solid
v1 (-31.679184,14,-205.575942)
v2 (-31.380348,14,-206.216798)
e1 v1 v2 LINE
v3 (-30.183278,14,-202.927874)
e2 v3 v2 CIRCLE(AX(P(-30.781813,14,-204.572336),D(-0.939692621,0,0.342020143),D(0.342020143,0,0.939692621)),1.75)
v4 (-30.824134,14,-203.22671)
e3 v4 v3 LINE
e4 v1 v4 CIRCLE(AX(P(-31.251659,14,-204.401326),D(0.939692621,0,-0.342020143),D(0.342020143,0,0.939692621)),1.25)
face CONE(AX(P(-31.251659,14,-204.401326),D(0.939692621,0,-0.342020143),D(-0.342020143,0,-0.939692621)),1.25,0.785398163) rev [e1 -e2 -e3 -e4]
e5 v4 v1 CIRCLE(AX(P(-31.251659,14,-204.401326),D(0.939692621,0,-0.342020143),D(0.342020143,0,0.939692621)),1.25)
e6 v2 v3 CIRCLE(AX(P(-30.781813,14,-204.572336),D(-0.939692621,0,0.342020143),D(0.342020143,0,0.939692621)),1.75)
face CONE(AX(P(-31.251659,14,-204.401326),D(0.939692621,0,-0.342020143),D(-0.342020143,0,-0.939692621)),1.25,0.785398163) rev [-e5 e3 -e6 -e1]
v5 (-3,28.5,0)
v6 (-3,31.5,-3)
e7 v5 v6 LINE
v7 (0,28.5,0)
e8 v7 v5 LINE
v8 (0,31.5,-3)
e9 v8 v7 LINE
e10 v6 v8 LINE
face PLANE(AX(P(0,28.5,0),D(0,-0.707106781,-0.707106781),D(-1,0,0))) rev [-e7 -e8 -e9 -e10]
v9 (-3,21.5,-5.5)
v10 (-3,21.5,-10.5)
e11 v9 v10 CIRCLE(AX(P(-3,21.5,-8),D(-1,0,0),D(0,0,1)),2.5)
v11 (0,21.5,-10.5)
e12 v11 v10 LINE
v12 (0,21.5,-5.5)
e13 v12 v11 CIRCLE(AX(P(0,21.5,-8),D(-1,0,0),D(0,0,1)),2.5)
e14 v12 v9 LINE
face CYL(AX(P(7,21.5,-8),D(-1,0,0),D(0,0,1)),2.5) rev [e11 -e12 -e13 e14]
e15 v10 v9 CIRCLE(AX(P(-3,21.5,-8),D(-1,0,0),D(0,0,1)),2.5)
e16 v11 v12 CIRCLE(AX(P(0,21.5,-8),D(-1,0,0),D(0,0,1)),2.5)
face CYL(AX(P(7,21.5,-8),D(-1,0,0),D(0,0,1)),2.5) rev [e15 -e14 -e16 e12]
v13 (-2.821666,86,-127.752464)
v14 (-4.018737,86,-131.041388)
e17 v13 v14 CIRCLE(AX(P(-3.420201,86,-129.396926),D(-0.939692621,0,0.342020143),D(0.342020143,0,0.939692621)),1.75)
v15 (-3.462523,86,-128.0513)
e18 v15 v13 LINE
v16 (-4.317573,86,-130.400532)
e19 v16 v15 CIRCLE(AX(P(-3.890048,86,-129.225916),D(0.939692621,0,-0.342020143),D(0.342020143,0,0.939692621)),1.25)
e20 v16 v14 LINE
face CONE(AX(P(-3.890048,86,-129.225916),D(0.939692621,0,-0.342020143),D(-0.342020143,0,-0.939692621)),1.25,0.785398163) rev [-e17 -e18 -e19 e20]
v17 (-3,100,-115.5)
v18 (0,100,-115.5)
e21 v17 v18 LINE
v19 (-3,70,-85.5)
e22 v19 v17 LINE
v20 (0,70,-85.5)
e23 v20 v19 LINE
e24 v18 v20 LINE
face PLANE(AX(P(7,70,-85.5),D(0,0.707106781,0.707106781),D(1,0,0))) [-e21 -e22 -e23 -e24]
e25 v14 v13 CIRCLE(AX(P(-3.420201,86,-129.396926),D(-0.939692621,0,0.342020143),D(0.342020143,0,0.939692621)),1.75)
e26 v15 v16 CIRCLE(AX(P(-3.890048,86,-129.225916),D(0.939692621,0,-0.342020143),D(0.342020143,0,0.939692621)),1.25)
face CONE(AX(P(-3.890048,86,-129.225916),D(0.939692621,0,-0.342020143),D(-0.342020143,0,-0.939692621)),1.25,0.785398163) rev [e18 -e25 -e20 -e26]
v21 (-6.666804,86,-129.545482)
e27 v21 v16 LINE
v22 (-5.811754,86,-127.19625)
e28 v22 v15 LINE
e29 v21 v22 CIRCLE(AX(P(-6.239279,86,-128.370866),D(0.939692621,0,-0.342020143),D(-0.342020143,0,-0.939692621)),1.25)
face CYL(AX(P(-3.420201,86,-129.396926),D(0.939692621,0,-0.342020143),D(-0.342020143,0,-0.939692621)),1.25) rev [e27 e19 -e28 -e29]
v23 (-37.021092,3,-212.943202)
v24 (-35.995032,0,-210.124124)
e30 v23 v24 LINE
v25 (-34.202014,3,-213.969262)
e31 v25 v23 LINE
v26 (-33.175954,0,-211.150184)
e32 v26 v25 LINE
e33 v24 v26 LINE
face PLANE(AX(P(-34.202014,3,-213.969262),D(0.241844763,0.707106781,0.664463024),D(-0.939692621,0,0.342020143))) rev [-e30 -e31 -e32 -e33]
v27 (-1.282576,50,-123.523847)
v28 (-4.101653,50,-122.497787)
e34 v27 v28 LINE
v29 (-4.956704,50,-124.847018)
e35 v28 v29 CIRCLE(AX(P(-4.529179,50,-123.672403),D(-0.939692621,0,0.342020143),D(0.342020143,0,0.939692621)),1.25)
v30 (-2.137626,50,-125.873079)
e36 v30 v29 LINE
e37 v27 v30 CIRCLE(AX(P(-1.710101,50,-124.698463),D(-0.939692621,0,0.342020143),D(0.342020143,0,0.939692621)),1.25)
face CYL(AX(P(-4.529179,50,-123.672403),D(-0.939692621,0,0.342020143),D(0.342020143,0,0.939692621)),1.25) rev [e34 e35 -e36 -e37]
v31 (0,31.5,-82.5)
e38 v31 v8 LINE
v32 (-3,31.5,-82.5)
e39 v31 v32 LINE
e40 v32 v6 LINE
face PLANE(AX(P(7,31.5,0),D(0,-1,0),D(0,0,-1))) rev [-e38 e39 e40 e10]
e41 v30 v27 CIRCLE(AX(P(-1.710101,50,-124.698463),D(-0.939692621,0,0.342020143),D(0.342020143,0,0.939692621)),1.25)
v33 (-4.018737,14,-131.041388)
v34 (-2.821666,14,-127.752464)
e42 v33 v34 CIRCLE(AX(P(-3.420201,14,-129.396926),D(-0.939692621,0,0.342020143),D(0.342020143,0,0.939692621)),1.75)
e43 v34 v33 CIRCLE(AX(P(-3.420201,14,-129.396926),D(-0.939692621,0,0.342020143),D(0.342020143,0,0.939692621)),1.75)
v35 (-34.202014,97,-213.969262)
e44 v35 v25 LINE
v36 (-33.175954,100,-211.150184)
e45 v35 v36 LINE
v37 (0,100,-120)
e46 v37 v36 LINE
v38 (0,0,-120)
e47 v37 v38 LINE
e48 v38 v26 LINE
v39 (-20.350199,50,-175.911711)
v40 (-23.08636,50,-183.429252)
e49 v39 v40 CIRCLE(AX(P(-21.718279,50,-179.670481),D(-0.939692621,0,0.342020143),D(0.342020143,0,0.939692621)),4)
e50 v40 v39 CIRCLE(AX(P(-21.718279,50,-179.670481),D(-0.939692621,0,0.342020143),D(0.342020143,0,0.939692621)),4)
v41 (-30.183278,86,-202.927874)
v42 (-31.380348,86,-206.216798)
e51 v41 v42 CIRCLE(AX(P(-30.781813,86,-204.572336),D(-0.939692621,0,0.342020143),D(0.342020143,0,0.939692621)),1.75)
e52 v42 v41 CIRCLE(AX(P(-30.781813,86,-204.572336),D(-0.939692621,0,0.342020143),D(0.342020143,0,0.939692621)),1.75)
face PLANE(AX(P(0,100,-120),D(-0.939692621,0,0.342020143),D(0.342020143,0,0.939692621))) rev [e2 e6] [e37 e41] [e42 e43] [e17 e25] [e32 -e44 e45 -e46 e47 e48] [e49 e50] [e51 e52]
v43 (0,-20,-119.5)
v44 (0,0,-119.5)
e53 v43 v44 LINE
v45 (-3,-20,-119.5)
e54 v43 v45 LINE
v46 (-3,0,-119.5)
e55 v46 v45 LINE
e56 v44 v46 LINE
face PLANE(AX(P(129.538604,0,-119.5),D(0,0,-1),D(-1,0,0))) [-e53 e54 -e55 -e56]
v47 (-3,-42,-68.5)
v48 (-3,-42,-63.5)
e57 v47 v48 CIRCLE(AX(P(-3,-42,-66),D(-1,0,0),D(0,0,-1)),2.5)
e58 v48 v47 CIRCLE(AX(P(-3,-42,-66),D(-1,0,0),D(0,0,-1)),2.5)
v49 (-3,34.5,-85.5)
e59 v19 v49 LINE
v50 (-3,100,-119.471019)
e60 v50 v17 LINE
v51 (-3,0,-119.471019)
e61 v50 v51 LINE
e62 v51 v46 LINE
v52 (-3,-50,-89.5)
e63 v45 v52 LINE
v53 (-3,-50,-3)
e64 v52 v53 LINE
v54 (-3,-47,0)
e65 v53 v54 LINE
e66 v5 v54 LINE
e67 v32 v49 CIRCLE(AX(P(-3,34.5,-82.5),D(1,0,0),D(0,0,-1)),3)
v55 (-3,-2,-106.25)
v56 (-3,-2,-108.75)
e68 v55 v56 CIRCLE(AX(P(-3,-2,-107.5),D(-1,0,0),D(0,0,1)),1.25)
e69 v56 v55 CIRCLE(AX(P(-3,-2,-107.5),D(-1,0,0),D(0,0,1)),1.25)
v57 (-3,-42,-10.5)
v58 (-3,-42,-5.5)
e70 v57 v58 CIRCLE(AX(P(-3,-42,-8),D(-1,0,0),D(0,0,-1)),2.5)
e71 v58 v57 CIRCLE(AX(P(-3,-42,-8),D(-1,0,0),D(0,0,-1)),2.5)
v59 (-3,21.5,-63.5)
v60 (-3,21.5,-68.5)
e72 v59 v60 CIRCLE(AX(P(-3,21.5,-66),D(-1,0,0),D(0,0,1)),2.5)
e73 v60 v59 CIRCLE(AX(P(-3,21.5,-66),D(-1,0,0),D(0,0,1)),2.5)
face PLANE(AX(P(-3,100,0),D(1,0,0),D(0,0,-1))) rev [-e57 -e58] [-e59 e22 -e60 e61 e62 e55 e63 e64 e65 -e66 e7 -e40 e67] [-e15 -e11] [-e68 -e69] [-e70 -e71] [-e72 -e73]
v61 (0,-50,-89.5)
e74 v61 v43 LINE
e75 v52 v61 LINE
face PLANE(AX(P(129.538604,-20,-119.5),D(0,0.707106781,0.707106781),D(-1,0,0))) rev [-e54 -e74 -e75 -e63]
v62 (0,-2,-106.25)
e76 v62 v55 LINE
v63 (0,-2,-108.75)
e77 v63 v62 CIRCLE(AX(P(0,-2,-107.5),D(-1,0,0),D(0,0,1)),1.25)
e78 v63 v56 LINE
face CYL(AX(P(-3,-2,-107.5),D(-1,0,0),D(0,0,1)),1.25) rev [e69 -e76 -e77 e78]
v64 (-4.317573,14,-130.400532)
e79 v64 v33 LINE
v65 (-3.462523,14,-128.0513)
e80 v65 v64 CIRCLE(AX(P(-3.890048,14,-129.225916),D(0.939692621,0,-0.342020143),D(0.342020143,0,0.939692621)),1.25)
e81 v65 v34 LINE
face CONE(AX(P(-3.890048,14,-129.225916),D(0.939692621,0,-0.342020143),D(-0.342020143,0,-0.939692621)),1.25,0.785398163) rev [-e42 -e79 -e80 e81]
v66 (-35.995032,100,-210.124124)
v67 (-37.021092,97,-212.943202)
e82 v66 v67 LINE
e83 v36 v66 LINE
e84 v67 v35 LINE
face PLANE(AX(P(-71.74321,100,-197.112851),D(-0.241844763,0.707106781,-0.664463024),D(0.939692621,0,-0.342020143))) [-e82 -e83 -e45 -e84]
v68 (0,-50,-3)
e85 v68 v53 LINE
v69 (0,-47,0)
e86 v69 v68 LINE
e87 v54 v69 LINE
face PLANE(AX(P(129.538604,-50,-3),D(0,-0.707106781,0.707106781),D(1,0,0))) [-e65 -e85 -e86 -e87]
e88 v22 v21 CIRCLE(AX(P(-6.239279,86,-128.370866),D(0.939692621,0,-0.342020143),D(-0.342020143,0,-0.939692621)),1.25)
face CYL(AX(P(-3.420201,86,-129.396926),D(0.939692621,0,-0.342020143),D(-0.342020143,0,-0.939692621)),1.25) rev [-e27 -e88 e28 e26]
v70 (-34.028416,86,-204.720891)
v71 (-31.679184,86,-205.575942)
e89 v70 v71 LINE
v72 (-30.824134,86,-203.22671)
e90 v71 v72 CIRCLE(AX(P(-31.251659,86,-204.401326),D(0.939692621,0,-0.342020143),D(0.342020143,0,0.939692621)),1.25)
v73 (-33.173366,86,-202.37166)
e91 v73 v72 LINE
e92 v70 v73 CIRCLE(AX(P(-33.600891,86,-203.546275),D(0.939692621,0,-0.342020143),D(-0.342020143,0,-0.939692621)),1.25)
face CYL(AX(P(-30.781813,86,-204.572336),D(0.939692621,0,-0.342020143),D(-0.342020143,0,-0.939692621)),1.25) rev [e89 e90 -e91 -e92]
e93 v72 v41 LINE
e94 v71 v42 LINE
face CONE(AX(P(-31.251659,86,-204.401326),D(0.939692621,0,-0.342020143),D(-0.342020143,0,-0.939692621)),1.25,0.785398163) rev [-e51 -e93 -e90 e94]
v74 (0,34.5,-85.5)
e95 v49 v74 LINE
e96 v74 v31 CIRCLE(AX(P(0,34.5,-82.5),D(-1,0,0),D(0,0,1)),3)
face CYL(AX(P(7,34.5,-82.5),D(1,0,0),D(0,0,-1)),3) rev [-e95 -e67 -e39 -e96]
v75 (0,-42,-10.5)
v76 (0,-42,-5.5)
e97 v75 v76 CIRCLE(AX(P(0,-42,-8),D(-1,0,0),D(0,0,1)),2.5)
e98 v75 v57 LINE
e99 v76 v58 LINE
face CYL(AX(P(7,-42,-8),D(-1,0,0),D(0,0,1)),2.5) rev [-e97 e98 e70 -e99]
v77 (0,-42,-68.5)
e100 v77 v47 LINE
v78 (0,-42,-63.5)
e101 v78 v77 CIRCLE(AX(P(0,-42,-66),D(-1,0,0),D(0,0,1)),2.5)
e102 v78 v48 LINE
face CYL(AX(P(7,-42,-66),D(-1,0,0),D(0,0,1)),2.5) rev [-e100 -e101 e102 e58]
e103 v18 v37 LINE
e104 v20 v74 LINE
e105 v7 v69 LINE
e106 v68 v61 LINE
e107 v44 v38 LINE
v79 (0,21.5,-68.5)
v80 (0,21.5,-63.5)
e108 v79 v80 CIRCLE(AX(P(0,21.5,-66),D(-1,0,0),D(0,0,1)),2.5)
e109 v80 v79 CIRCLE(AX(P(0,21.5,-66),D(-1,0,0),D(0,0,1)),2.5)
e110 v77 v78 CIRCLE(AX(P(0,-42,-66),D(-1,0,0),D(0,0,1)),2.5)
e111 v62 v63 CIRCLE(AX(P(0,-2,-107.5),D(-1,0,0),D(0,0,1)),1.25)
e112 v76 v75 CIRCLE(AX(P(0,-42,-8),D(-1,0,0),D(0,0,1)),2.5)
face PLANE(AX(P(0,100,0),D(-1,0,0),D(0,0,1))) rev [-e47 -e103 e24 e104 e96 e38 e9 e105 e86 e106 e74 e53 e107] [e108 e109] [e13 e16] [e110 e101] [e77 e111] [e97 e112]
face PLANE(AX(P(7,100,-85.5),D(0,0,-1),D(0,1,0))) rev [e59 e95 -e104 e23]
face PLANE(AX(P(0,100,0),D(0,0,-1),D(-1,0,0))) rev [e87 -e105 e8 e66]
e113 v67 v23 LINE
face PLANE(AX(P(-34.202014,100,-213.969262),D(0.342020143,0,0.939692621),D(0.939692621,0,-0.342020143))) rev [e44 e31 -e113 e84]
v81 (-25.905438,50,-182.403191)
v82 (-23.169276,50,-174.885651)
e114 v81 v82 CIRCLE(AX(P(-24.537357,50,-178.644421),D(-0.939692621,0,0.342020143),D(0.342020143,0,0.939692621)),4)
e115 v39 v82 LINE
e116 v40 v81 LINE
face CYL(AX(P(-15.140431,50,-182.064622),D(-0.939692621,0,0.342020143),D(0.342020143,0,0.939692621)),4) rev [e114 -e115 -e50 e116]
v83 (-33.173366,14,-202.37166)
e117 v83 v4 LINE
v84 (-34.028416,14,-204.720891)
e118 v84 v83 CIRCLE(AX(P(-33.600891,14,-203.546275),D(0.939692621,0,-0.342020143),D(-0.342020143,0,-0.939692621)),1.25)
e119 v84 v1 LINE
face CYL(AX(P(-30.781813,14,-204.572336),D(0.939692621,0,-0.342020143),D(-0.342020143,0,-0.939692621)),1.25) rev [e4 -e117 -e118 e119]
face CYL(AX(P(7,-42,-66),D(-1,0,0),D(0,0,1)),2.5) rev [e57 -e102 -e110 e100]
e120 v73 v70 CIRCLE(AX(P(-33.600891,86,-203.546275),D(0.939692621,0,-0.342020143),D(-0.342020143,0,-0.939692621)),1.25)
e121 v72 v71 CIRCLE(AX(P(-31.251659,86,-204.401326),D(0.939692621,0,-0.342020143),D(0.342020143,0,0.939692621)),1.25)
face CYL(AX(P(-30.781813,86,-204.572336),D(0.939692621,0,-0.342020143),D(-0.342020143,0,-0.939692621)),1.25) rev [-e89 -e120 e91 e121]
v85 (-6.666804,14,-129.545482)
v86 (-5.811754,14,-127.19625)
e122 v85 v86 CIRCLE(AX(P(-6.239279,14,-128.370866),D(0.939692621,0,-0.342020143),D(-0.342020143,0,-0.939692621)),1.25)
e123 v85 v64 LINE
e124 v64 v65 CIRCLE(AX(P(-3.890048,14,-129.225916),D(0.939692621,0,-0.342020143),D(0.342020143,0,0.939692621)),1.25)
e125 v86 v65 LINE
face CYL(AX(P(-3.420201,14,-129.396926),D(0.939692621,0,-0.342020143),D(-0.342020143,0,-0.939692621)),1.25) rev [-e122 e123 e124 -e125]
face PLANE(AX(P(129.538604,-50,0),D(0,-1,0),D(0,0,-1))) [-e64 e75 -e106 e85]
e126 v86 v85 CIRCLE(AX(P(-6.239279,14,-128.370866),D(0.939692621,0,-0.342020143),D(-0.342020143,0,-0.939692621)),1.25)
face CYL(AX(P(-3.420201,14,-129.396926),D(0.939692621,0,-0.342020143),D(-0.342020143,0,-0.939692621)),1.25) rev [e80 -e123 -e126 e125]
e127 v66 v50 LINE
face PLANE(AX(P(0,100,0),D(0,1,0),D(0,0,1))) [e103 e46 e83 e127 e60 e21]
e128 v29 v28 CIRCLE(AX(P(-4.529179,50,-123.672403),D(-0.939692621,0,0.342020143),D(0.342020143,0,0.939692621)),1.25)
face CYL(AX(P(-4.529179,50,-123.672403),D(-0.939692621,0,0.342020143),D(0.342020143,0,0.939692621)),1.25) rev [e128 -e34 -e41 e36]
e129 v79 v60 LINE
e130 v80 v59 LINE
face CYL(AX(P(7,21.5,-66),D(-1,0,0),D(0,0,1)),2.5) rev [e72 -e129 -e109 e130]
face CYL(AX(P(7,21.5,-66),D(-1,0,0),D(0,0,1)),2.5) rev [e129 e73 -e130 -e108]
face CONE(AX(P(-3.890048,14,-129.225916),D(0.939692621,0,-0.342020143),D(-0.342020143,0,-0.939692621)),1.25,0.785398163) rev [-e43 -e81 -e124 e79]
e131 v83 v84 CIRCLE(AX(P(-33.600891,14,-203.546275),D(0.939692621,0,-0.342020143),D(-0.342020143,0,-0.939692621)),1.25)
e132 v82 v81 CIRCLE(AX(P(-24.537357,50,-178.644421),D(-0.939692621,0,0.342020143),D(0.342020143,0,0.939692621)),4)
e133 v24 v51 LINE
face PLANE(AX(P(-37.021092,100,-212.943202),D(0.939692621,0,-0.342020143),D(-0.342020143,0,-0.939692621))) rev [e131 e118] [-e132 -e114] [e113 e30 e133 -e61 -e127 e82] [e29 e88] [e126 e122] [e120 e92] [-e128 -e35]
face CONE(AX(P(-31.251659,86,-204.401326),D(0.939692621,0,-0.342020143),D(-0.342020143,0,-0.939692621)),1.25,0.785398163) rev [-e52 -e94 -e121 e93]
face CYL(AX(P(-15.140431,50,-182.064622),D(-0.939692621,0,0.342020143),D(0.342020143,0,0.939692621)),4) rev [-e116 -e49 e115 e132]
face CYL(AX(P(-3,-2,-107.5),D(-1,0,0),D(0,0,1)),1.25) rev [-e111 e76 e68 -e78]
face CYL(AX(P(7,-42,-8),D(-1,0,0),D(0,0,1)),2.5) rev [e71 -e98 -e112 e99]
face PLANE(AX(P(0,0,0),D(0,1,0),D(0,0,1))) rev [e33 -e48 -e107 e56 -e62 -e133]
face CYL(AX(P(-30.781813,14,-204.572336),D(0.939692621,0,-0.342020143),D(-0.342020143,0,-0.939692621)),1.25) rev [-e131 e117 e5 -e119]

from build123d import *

# Parameters (mm, degrees)
BOSS_EXTRUDE1_DEPTH   = 100
SKETCH3_R             = 1
CUT_EXTRUDE2_DEPTH    = 10
LPATTERN1_COUNT       = 2
LPATTERN1_PITCH       = 80
M3_TAPPED_HOLE1_D     = 2.5
M3_TAPPED_HOLE1_DEPTH = 7.5
M3_TAPPED_HOLE1_TIP   = 0.751075774
CHAMFER2_SIZE         = 0.5
SKETCH6_W             = 85.5
SKETCH6_H             = 68.5
CUT_EXTRUDE4_DEPTH    = 10
CHAMFER3_SIZE         = 30
FILLET1_R             = 3
SKETCH7_R             = 4
CUT_EXTRUDE5_DEPTH    = 10
SKETCH9_W             = 119.5
SKETCH9_H             = 50
BOSS_EXTRUDE2_DEPTH   = 3
SKETCH5_R             = 2.5
CUT_EXTRUDE3_DEPTH    = 10
CHAMFER4_SIZE         = 3
CHAMFER5_SIZE         = 30
M3_TAPPED_HOLE2_D     = 2.5
M3_TAPPED_HOLE2_DEPTH = 7.5
M3_TAPPED_HOLE2_TIP   = 0.751075774
M3_TAPPED_HOLE3_D     = 2.5
M3_TAPPED_HOLE3_DEPTH = 7.5
M3_TAPPED_HOLE3_TIP   = 0.751075774


with BuildPart() as part:
    # Sketch1 → Boss-Extrude1 (new body)
    with BuildSketch(Plane(origin=(0, 0, 0), x_dir=(1, 0, 0), z_dir=(0, 1, 0))):
        Polygon((0, 120), (-34.202014333, 213.969262079), (-37.021092195, 212.943201649), (-3, 119.471019058), (-3, 0), (0, 0), align=None)
    extrude(amount=BOSS_EXTRUDE1_DEPTH)

    # Sketch3 → Cut-Extrude2 (cut)
    with BuildSketch(Plane(origin=(35.748178719, 0, -13.011272983), x_dir=(0.3420201433256699, 0, 0.939692620785908), z_dir=(-0.9396926207859081, 0, 0.3420201433256699))):
        with Locations((-202.763114494, 86)):
            Circle(SKETCH3_R)
        with Locations((-202.763114494, 14)):
            Circle(SKETCH3_R)
    cut_extrude2 = extrude(amount=-CUT_EXTRUDE2_DEPTH, mode=Mode.SUBTRACT)

    # LPattern1: Cut-Extrude2 ×2
    with Locations(*[Vector(0.3420201433256699, 0, 0.939692620785908) * (i * LPATTERN1_PITCH) for i in range(1, LPATTERN1_COUNT)]):
        add(cut_extrude2, mode=Mode.SUBTRACT)

    # M3 Tapped Hole1
    with Locations(Plane(origin=(-30.781812899, 86, -204.572335871), x_dir=(0.342020143326, 0, 0.939692620786), z_dir=(0.939692620786, 0, -0.342020143326))):
        with Locations((0, 0), (0, 72), (80, 72), (80, 0)):
            Hole(M3_TAPPED_HOLE1_D / 2, depth=M3_TAPPED_HOLE1_DEPTH)
            with Locations((0, 0, -(M3_TAPPED_HOLE1_DEPTH + M3_TAPPED_HOLE1_TIP / 2))):  # 118° drill point
                Cone(0, M3_TAPPED_HOLE1_D / 2, M3_TAPPED_HOLE1_TIP, mode=Mode.SUBTRACT)

    # Chamfer2
    chamfer2_edges = [part.edges().sort_by_distance(p)[0] for p in [
        (-2.992676254, 86, -128.222310432),
        (-2.992676254, 14, -128.222310432),
        (-30.35428772, 14, -203.397720095),
        (-30.35428772, 86, -203.397720095),
    ]]
    chamfer(chamfer2_edges, length=CHAMFER2_SIZE)

    # Sketch6 → Cut-Extrude4 (cut)
    with BuildSketch(Plane.ZY.offset(3)):
        with Locations((-42.75, 65.75)):
            Rectangle(SKETCH6_W, SKETCH6_H)
    extrude(amount=-CUT_EXTRUDE4_DEPTH, mode=Mode.SUBTRACT)

    # Chamfer3
    chamfer3_edges = [part.edges().sort_by_distance(p)[0] for p in [
        (-1.5, 100, -85.5),
    ]]
    chamfer(chamfer3_edges, length=CHAMFER3_SIZE)

    # Fillet1
    fillet1_edges = [part.edges().sort_by_distance(p)[0] for p in [
        (-1.5, 31.5, -85.5),
    ]]
    fillet(fillet1_edges, radius=FILLET1_R)

    # Sketch7 → Cut-Extrude5 (cut)
    with BuildSketch(Plane(origin=(35.748178719, 0, -13.011272983), x_dir=(0.3420201433256699, 0, 0.939692620785908), z_dir=(-0.9396926207859081, 0, 0.3420201433256699))):
        with Locations((-176.263114494, 50)):
            Circle(SKETCH7_R)
    extrude(amount=-CUT_EXTRUDE5_DEPTH, mode=Mode.SUBTRACT)

    # Sketch9 → Boss-Extrude2 (add)
    with BuildSketch(Plane.ZY.offset(3)):
        with Locations((-59.75, -25)):
            Rectangle(SKETCH9_W, SKETCH9_H)
    extrude(amount=-BOSS_EXTRUDE2_DEPTH)

    # Sketch5 → Cut-Extrude3 (cut)
    with BuildSketch(Plane.ZY.offset(3)):
        with Locations((-8, 21.5)):
            Circle(SKETCH5_R)
        with Locations((-8, -42)):
            Circle(SKETCH5_R)
        with Locations((-66, 21.5)):
            Circle(SKETCH5_R)
        with Locations((-66, -42)):
            Circle(SKETCH5_R)
    extrude(amount=-CUT_EXTRUDE3_DEPTH, mode=Mode.SUBTRACT)

    # Chamfer4
    chamfer4_edges = [part.edges().sort_by_distance(p)[0] for p in [
        (-1.5, 31.5, 0),
        (-35.611553264, 100, -213.456231864),
        (-35.611553264, 0, -213.456231864),
        (-1.5, -50, 0),
    ]]
    chamfer(chamfer4_edges, length=CHAMFER4_SIZE)

    # Chamfer5
    chamfer5_edges = [part.edges().sort_by_distance(p)[0] for p in [
        (-1.5, -50, -119.5),
    ]]
    chamfer(chamfer5_edges, length=CHAMFER5_SIZE)

    # M3 Tapped Hole2
    with Locations(Plane(origin=(35.748178719, 0, -13.011272983), x_dir=(0.3420201433256699, 0, 0.939692620785908), z_dir=(-0.9396926207859081, 0, 0.3420201433256699))):
        with Locations((-117.763114494, 50)):
            Hole(M3_TAPPED_HOLE2_D / 2, depth=M3_TAPPED_HOLE2_DEPTH)
            with Locations((0, 0, -(M3_TAPPED_HOLE2_DEPTH + M3_TAPPED_HOLE2_TIP / 2))):  # 118° drill point
                Cone(0, M3_TAPPED_HOLE2_D / 2, M3_TAPPED_HOLE2_TIP, mode=Mode.SUBTRACT)

    # M3 Tapped Hole3
    with Locations(Plane.ZY.offset(3)):
        with Locations((-107.5, -2)):
            Hole(M3_TAPPED_HOLE3_D / 2, depth=M3_TAPPED_HOLE3_DEPTH)
            with Locations((0, 0, -(M3_TAPPED_HOLE3_DEPTH + M3_TAPPED_HOLE3_TIP / 2))):  # 118° drill point
                Cone(0, M3_TAPPED_HOLE3_D / 2, M3_TAPPED_HOLE3_TIP, mode=Mode.SUBTRACT)


solid = part.part
